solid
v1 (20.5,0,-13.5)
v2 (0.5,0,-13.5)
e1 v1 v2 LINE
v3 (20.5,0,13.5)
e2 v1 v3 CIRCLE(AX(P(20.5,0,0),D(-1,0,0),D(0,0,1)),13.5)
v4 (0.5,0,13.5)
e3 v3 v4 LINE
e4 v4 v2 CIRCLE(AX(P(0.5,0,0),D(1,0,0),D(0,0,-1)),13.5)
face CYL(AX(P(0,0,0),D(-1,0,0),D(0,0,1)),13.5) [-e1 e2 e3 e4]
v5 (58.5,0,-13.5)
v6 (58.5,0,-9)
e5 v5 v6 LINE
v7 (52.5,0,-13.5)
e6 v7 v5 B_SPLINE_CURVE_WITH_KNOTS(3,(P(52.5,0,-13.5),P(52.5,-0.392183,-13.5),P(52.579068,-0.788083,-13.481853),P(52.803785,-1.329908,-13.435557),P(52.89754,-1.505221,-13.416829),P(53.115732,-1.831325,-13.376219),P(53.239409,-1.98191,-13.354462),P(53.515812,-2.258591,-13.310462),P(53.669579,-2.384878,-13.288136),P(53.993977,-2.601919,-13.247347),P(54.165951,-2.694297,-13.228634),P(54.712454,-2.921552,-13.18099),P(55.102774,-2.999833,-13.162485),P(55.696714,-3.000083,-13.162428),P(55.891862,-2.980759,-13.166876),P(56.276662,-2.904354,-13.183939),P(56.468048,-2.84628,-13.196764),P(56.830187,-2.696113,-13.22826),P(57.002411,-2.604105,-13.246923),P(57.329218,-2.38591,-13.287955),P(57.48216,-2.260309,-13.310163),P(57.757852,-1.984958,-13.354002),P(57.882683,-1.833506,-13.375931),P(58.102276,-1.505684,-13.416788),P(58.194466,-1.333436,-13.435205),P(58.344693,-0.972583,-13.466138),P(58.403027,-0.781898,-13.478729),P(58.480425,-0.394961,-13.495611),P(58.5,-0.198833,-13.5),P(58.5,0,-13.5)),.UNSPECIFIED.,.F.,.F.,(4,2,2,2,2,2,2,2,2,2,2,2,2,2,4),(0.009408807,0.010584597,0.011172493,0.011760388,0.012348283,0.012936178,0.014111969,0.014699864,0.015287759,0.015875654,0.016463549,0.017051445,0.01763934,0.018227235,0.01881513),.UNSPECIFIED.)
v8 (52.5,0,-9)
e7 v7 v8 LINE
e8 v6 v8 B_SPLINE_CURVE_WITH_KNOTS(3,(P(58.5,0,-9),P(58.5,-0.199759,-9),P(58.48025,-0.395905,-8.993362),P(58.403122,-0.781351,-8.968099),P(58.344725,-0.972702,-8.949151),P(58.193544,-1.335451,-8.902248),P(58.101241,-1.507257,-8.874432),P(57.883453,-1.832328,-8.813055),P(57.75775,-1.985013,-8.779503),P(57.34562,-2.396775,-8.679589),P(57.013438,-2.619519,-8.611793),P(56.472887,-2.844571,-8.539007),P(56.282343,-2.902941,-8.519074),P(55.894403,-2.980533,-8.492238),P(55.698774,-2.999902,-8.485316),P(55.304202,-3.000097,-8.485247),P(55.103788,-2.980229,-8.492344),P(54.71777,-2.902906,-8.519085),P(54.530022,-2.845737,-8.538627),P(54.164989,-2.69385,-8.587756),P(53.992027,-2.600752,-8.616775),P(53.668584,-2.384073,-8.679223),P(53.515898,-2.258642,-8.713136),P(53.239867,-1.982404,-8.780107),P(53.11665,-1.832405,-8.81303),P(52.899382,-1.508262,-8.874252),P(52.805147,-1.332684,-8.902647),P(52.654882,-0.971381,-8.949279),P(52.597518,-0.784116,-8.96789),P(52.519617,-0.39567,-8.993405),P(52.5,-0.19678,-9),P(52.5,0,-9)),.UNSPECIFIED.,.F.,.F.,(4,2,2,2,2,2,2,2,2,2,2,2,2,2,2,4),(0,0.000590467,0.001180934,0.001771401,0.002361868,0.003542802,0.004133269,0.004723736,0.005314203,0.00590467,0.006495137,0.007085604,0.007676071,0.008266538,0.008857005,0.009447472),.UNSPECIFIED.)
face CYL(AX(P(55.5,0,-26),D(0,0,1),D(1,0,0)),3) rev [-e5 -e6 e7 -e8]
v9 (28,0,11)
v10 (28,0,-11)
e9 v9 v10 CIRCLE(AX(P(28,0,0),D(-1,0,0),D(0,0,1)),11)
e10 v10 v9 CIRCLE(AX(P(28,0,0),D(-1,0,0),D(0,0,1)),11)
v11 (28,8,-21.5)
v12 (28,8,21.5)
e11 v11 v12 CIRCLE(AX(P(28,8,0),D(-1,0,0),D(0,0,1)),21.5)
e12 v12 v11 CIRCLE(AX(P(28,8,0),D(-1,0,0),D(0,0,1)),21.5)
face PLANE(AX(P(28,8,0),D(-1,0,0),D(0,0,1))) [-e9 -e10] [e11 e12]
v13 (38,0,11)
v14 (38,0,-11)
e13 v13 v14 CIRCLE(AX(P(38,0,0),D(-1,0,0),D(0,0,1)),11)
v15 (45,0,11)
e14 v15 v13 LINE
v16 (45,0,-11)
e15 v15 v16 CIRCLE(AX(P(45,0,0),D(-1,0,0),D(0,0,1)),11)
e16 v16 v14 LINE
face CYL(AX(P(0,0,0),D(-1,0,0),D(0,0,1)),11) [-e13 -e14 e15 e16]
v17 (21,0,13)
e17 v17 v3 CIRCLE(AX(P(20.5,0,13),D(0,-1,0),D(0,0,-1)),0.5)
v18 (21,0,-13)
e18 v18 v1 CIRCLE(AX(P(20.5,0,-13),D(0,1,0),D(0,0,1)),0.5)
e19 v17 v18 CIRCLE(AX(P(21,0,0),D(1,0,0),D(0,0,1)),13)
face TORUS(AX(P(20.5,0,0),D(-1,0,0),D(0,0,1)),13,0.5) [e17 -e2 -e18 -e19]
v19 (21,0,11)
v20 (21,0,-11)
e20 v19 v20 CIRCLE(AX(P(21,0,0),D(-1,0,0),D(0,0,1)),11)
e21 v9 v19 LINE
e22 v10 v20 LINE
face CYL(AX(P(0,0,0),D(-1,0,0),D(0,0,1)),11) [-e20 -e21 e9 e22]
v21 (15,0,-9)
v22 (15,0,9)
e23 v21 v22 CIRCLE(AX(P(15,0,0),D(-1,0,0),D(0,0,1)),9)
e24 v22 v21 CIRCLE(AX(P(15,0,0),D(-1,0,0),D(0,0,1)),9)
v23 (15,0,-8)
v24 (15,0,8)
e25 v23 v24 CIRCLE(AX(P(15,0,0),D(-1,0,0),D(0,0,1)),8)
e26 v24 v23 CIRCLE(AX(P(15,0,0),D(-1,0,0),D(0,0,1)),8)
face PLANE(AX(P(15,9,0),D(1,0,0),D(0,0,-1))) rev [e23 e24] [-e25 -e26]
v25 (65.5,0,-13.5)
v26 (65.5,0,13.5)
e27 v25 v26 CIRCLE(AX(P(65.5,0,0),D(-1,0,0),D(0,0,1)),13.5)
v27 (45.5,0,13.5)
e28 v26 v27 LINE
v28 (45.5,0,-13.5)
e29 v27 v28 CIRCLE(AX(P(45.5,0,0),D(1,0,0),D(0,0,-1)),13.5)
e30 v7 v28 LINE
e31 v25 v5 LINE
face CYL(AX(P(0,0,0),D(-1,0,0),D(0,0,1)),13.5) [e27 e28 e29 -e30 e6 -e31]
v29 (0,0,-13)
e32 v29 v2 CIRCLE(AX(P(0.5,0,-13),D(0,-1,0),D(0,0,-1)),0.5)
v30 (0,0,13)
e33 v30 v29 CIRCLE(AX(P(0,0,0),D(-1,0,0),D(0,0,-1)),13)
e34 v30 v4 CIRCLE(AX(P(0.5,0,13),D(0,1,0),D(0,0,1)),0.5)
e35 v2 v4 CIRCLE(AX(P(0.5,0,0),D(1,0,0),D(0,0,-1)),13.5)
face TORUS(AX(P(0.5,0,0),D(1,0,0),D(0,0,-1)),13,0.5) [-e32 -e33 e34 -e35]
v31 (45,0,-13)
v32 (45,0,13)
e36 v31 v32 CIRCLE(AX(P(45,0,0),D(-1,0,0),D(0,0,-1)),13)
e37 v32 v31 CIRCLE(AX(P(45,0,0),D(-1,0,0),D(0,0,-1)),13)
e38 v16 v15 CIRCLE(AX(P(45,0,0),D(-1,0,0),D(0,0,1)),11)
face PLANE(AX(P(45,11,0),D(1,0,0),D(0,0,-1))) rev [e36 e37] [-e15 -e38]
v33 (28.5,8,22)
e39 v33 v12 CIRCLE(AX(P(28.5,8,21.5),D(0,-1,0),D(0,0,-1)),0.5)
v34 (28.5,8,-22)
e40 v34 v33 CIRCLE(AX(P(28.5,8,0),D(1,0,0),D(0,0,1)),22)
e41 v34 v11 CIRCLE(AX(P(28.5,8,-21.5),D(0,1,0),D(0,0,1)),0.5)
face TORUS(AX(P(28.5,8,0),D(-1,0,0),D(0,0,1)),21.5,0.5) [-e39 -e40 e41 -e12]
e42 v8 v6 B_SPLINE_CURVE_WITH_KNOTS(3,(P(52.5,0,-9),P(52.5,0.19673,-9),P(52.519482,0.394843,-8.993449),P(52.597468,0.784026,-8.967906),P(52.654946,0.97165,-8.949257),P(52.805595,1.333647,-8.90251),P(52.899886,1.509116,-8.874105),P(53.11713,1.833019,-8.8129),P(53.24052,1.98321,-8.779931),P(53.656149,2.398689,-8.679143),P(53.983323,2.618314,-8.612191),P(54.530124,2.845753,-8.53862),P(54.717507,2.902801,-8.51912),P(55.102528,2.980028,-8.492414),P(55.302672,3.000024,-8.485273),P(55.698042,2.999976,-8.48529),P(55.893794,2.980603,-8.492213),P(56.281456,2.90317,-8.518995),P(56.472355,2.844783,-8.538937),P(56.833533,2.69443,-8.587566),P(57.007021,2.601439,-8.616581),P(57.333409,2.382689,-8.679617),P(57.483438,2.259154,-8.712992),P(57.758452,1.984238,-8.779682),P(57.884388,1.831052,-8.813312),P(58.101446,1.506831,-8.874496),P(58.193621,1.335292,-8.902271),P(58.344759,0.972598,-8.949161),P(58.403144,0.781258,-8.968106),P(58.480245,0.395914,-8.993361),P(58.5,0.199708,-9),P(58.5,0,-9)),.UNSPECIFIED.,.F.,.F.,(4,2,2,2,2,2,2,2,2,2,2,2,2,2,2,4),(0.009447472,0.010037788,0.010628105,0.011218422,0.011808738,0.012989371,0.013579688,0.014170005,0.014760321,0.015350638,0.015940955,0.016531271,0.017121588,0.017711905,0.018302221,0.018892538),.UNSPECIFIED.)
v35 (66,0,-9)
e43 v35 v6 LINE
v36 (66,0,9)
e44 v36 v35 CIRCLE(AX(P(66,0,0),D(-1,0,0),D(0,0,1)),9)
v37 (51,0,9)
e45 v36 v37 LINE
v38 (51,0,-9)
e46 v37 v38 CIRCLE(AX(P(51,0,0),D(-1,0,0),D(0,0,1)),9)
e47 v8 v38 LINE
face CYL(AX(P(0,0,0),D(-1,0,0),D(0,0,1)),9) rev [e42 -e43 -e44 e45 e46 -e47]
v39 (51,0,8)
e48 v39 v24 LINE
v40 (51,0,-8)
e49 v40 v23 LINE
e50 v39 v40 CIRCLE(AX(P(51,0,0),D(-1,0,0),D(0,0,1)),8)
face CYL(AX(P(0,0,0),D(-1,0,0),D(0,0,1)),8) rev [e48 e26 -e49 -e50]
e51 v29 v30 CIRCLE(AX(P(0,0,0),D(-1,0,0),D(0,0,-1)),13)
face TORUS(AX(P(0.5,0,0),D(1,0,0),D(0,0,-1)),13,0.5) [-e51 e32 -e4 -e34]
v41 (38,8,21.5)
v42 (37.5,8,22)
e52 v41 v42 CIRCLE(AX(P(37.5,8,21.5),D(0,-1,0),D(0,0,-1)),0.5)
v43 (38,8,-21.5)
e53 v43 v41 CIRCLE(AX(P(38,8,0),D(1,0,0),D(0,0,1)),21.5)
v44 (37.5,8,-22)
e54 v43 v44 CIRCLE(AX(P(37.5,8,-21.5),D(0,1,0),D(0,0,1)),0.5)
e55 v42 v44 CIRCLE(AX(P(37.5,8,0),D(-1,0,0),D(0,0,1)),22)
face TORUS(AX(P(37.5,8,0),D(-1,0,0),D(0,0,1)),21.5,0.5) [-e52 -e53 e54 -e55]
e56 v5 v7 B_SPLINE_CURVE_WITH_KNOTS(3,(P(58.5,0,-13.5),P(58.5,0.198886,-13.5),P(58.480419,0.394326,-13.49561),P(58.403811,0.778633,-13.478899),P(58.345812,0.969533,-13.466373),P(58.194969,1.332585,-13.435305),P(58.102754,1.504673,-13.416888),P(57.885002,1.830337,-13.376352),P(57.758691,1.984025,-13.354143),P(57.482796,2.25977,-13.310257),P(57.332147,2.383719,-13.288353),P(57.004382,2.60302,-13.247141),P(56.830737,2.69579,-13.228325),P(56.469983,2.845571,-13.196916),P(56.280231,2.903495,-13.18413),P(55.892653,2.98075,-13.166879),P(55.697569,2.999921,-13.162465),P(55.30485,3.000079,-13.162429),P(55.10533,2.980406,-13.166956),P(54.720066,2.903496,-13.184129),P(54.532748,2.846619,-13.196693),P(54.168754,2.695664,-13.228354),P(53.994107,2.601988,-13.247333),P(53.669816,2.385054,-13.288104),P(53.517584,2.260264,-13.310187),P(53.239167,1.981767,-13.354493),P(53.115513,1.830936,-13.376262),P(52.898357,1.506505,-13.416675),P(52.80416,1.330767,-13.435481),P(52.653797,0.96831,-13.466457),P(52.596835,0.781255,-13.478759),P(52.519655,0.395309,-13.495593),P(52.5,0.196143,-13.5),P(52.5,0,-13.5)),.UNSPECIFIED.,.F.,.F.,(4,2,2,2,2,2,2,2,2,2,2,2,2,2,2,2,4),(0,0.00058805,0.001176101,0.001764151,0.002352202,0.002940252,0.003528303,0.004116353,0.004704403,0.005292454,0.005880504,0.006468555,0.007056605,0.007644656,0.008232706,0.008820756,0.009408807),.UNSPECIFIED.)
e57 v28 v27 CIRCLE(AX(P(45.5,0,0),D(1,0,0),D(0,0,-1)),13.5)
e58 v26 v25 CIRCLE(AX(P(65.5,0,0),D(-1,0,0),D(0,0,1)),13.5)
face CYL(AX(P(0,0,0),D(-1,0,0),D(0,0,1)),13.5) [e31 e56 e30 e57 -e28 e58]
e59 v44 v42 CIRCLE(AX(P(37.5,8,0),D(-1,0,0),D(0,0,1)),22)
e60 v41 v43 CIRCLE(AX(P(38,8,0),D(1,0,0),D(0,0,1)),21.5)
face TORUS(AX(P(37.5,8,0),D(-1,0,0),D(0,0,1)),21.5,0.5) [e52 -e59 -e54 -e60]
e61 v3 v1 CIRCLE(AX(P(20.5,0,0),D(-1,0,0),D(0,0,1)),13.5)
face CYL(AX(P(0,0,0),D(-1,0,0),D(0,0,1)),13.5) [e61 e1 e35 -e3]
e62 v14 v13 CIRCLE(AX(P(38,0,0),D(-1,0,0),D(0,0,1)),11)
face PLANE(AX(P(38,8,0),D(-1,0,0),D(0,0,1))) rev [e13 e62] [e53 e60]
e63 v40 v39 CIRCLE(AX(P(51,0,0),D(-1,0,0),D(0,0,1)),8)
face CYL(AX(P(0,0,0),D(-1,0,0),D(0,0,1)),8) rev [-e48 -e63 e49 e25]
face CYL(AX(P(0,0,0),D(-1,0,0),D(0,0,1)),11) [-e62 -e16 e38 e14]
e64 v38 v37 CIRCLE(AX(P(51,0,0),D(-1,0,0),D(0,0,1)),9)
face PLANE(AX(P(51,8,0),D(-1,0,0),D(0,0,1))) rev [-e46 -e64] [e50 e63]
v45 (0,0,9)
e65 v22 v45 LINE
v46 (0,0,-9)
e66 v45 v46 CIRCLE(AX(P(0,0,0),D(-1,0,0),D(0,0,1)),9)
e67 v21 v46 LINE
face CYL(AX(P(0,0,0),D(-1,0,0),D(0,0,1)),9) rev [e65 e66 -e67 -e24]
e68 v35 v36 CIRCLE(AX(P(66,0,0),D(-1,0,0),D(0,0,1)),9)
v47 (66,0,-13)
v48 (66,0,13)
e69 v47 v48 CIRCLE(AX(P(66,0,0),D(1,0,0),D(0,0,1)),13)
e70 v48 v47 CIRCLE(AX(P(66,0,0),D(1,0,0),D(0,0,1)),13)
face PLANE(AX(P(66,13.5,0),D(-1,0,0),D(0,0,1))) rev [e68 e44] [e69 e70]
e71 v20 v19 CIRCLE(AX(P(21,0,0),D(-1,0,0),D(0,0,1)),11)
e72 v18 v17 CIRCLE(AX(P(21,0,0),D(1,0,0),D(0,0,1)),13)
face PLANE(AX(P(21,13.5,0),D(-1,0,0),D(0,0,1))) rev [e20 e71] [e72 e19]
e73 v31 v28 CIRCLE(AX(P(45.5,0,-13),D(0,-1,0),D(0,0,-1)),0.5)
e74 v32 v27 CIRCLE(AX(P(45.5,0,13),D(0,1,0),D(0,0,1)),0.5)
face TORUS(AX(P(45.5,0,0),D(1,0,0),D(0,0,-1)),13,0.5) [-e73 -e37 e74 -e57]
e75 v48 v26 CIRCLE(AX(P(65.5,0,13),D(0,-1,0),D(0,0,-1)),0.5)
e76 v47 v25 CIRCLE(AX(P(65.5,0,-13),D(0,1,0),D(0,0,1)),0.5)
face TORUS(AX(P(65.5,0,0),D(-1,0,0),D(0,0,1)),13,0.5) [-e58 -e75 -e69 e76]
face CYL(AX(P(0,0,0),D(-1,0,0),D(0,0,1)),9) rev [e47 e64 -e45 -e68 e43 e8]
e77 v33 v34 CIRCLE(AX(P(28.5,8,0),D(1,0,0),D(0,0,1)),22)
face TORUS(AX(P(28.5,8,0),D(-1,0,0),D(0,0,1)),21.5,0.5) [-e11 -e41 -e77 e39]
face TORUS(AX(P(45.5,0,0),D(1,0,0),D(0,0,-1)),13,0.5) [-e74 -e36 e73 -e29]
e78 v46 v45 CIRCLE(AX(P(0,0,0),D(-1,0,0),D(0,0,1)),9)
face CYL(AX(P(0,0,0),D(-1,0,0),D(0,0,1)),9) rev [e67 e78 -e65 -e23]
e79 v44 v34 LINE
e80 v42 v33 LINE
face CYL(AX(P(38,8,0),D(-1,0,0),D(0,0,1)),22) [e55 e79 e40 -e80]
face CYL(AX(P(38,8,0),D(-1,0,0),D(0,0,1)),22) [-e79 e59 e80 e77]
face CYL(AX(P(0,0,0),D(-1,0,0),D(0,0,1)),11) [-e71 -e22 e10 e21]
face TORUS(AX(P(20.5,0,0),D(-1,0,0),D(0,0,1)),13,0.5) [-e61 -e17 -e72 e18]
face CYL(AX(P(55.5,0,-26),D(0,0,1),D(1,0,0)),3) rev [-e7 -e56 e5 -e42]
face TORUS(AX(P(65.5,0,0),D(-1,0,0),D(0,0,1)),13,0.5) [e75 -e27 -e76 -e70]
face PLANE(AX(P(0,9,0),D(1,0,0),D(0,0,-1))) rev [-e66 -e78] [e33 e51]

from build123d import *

# Parameters (mm, degrees)
SKETCH2_R           = 22
BOSS_EXTRUDE1_DEPTH = 5
SKETCH3_R           = 8
CUT_EXTRUDE1_DEPTH  = 13
FILLET1_R           = 0.5
SKETCH4_R           = 3
CUT_EXTRUDE2_DEPTH  = 26


with BuildPart() as part:
    # Sketch1 → Revolve1 (revolve)
    with BuildSketch(Plane.XY, mode=Mode.PRIVATE) as revolve1_sk:
        Polygon((0, 9), (0, 13.5), (21, 13.5), (21, 11), (45, 11), (45, 13.5), (66, 13.5), (66, 9), (51, 9), (51, 8), (15, 8), (15, 9), align=None)
    revolve(revolve1_sk.sketch.rotate(Axis((0, 0, 0), (1, 0, 0)), 90), axis=Axis((0, 0, 0), (1, 0, 0)))

    # Sketch2 → Boss-Extrude1 (add, symmetric)
    with BuildSketch(Plane.ZY.offset(-33)):
        with Locations((0, 8)):
            Circle(SKETCH2_R)
    extrude(amount=BOSS_EXTRUDE1_DEPTH, both=True)

    # Sketch3 → Cut-Extrude1 (cut, symmetric)
    with BuildSketch(Plane(origin=(38, 0, 0), x_dir=(0, 0, -1), z_dir=(1, 0, 0))):
        with Locations(Location((0, 0, 0), (0, 0, 180))):
            Circle(SKETCH3_R)
    extrude(amount=CUT_EXTRUDE1_DEPTH, both=True, mode=Mode.SUBTRACT)

    # Fillet1
    fillet1_edges = [part.edges().sort_by_distance(p)[0] for p in [
        (66, 0, -13.5),
        (45, 0, -13.5),
        (21, 0, -13.5),
        (0, 0, -13.5),
        (28, 8, -22),
        (38, 8, -22),
    ]]
    fillet(fillet1_edges, radius=FILLET1_R)

    # Sketch4 → Cut-Extrude2 (cut)
    with BuildSketch(Plane.XY):
        with Locations((55.5, 0)):
            Circle(SKETCH4_R)
    extrude(amount=-CUT_EXTRUDE2_DEPTH, mode=Mode.SUBTRACT)


solid = part.part
